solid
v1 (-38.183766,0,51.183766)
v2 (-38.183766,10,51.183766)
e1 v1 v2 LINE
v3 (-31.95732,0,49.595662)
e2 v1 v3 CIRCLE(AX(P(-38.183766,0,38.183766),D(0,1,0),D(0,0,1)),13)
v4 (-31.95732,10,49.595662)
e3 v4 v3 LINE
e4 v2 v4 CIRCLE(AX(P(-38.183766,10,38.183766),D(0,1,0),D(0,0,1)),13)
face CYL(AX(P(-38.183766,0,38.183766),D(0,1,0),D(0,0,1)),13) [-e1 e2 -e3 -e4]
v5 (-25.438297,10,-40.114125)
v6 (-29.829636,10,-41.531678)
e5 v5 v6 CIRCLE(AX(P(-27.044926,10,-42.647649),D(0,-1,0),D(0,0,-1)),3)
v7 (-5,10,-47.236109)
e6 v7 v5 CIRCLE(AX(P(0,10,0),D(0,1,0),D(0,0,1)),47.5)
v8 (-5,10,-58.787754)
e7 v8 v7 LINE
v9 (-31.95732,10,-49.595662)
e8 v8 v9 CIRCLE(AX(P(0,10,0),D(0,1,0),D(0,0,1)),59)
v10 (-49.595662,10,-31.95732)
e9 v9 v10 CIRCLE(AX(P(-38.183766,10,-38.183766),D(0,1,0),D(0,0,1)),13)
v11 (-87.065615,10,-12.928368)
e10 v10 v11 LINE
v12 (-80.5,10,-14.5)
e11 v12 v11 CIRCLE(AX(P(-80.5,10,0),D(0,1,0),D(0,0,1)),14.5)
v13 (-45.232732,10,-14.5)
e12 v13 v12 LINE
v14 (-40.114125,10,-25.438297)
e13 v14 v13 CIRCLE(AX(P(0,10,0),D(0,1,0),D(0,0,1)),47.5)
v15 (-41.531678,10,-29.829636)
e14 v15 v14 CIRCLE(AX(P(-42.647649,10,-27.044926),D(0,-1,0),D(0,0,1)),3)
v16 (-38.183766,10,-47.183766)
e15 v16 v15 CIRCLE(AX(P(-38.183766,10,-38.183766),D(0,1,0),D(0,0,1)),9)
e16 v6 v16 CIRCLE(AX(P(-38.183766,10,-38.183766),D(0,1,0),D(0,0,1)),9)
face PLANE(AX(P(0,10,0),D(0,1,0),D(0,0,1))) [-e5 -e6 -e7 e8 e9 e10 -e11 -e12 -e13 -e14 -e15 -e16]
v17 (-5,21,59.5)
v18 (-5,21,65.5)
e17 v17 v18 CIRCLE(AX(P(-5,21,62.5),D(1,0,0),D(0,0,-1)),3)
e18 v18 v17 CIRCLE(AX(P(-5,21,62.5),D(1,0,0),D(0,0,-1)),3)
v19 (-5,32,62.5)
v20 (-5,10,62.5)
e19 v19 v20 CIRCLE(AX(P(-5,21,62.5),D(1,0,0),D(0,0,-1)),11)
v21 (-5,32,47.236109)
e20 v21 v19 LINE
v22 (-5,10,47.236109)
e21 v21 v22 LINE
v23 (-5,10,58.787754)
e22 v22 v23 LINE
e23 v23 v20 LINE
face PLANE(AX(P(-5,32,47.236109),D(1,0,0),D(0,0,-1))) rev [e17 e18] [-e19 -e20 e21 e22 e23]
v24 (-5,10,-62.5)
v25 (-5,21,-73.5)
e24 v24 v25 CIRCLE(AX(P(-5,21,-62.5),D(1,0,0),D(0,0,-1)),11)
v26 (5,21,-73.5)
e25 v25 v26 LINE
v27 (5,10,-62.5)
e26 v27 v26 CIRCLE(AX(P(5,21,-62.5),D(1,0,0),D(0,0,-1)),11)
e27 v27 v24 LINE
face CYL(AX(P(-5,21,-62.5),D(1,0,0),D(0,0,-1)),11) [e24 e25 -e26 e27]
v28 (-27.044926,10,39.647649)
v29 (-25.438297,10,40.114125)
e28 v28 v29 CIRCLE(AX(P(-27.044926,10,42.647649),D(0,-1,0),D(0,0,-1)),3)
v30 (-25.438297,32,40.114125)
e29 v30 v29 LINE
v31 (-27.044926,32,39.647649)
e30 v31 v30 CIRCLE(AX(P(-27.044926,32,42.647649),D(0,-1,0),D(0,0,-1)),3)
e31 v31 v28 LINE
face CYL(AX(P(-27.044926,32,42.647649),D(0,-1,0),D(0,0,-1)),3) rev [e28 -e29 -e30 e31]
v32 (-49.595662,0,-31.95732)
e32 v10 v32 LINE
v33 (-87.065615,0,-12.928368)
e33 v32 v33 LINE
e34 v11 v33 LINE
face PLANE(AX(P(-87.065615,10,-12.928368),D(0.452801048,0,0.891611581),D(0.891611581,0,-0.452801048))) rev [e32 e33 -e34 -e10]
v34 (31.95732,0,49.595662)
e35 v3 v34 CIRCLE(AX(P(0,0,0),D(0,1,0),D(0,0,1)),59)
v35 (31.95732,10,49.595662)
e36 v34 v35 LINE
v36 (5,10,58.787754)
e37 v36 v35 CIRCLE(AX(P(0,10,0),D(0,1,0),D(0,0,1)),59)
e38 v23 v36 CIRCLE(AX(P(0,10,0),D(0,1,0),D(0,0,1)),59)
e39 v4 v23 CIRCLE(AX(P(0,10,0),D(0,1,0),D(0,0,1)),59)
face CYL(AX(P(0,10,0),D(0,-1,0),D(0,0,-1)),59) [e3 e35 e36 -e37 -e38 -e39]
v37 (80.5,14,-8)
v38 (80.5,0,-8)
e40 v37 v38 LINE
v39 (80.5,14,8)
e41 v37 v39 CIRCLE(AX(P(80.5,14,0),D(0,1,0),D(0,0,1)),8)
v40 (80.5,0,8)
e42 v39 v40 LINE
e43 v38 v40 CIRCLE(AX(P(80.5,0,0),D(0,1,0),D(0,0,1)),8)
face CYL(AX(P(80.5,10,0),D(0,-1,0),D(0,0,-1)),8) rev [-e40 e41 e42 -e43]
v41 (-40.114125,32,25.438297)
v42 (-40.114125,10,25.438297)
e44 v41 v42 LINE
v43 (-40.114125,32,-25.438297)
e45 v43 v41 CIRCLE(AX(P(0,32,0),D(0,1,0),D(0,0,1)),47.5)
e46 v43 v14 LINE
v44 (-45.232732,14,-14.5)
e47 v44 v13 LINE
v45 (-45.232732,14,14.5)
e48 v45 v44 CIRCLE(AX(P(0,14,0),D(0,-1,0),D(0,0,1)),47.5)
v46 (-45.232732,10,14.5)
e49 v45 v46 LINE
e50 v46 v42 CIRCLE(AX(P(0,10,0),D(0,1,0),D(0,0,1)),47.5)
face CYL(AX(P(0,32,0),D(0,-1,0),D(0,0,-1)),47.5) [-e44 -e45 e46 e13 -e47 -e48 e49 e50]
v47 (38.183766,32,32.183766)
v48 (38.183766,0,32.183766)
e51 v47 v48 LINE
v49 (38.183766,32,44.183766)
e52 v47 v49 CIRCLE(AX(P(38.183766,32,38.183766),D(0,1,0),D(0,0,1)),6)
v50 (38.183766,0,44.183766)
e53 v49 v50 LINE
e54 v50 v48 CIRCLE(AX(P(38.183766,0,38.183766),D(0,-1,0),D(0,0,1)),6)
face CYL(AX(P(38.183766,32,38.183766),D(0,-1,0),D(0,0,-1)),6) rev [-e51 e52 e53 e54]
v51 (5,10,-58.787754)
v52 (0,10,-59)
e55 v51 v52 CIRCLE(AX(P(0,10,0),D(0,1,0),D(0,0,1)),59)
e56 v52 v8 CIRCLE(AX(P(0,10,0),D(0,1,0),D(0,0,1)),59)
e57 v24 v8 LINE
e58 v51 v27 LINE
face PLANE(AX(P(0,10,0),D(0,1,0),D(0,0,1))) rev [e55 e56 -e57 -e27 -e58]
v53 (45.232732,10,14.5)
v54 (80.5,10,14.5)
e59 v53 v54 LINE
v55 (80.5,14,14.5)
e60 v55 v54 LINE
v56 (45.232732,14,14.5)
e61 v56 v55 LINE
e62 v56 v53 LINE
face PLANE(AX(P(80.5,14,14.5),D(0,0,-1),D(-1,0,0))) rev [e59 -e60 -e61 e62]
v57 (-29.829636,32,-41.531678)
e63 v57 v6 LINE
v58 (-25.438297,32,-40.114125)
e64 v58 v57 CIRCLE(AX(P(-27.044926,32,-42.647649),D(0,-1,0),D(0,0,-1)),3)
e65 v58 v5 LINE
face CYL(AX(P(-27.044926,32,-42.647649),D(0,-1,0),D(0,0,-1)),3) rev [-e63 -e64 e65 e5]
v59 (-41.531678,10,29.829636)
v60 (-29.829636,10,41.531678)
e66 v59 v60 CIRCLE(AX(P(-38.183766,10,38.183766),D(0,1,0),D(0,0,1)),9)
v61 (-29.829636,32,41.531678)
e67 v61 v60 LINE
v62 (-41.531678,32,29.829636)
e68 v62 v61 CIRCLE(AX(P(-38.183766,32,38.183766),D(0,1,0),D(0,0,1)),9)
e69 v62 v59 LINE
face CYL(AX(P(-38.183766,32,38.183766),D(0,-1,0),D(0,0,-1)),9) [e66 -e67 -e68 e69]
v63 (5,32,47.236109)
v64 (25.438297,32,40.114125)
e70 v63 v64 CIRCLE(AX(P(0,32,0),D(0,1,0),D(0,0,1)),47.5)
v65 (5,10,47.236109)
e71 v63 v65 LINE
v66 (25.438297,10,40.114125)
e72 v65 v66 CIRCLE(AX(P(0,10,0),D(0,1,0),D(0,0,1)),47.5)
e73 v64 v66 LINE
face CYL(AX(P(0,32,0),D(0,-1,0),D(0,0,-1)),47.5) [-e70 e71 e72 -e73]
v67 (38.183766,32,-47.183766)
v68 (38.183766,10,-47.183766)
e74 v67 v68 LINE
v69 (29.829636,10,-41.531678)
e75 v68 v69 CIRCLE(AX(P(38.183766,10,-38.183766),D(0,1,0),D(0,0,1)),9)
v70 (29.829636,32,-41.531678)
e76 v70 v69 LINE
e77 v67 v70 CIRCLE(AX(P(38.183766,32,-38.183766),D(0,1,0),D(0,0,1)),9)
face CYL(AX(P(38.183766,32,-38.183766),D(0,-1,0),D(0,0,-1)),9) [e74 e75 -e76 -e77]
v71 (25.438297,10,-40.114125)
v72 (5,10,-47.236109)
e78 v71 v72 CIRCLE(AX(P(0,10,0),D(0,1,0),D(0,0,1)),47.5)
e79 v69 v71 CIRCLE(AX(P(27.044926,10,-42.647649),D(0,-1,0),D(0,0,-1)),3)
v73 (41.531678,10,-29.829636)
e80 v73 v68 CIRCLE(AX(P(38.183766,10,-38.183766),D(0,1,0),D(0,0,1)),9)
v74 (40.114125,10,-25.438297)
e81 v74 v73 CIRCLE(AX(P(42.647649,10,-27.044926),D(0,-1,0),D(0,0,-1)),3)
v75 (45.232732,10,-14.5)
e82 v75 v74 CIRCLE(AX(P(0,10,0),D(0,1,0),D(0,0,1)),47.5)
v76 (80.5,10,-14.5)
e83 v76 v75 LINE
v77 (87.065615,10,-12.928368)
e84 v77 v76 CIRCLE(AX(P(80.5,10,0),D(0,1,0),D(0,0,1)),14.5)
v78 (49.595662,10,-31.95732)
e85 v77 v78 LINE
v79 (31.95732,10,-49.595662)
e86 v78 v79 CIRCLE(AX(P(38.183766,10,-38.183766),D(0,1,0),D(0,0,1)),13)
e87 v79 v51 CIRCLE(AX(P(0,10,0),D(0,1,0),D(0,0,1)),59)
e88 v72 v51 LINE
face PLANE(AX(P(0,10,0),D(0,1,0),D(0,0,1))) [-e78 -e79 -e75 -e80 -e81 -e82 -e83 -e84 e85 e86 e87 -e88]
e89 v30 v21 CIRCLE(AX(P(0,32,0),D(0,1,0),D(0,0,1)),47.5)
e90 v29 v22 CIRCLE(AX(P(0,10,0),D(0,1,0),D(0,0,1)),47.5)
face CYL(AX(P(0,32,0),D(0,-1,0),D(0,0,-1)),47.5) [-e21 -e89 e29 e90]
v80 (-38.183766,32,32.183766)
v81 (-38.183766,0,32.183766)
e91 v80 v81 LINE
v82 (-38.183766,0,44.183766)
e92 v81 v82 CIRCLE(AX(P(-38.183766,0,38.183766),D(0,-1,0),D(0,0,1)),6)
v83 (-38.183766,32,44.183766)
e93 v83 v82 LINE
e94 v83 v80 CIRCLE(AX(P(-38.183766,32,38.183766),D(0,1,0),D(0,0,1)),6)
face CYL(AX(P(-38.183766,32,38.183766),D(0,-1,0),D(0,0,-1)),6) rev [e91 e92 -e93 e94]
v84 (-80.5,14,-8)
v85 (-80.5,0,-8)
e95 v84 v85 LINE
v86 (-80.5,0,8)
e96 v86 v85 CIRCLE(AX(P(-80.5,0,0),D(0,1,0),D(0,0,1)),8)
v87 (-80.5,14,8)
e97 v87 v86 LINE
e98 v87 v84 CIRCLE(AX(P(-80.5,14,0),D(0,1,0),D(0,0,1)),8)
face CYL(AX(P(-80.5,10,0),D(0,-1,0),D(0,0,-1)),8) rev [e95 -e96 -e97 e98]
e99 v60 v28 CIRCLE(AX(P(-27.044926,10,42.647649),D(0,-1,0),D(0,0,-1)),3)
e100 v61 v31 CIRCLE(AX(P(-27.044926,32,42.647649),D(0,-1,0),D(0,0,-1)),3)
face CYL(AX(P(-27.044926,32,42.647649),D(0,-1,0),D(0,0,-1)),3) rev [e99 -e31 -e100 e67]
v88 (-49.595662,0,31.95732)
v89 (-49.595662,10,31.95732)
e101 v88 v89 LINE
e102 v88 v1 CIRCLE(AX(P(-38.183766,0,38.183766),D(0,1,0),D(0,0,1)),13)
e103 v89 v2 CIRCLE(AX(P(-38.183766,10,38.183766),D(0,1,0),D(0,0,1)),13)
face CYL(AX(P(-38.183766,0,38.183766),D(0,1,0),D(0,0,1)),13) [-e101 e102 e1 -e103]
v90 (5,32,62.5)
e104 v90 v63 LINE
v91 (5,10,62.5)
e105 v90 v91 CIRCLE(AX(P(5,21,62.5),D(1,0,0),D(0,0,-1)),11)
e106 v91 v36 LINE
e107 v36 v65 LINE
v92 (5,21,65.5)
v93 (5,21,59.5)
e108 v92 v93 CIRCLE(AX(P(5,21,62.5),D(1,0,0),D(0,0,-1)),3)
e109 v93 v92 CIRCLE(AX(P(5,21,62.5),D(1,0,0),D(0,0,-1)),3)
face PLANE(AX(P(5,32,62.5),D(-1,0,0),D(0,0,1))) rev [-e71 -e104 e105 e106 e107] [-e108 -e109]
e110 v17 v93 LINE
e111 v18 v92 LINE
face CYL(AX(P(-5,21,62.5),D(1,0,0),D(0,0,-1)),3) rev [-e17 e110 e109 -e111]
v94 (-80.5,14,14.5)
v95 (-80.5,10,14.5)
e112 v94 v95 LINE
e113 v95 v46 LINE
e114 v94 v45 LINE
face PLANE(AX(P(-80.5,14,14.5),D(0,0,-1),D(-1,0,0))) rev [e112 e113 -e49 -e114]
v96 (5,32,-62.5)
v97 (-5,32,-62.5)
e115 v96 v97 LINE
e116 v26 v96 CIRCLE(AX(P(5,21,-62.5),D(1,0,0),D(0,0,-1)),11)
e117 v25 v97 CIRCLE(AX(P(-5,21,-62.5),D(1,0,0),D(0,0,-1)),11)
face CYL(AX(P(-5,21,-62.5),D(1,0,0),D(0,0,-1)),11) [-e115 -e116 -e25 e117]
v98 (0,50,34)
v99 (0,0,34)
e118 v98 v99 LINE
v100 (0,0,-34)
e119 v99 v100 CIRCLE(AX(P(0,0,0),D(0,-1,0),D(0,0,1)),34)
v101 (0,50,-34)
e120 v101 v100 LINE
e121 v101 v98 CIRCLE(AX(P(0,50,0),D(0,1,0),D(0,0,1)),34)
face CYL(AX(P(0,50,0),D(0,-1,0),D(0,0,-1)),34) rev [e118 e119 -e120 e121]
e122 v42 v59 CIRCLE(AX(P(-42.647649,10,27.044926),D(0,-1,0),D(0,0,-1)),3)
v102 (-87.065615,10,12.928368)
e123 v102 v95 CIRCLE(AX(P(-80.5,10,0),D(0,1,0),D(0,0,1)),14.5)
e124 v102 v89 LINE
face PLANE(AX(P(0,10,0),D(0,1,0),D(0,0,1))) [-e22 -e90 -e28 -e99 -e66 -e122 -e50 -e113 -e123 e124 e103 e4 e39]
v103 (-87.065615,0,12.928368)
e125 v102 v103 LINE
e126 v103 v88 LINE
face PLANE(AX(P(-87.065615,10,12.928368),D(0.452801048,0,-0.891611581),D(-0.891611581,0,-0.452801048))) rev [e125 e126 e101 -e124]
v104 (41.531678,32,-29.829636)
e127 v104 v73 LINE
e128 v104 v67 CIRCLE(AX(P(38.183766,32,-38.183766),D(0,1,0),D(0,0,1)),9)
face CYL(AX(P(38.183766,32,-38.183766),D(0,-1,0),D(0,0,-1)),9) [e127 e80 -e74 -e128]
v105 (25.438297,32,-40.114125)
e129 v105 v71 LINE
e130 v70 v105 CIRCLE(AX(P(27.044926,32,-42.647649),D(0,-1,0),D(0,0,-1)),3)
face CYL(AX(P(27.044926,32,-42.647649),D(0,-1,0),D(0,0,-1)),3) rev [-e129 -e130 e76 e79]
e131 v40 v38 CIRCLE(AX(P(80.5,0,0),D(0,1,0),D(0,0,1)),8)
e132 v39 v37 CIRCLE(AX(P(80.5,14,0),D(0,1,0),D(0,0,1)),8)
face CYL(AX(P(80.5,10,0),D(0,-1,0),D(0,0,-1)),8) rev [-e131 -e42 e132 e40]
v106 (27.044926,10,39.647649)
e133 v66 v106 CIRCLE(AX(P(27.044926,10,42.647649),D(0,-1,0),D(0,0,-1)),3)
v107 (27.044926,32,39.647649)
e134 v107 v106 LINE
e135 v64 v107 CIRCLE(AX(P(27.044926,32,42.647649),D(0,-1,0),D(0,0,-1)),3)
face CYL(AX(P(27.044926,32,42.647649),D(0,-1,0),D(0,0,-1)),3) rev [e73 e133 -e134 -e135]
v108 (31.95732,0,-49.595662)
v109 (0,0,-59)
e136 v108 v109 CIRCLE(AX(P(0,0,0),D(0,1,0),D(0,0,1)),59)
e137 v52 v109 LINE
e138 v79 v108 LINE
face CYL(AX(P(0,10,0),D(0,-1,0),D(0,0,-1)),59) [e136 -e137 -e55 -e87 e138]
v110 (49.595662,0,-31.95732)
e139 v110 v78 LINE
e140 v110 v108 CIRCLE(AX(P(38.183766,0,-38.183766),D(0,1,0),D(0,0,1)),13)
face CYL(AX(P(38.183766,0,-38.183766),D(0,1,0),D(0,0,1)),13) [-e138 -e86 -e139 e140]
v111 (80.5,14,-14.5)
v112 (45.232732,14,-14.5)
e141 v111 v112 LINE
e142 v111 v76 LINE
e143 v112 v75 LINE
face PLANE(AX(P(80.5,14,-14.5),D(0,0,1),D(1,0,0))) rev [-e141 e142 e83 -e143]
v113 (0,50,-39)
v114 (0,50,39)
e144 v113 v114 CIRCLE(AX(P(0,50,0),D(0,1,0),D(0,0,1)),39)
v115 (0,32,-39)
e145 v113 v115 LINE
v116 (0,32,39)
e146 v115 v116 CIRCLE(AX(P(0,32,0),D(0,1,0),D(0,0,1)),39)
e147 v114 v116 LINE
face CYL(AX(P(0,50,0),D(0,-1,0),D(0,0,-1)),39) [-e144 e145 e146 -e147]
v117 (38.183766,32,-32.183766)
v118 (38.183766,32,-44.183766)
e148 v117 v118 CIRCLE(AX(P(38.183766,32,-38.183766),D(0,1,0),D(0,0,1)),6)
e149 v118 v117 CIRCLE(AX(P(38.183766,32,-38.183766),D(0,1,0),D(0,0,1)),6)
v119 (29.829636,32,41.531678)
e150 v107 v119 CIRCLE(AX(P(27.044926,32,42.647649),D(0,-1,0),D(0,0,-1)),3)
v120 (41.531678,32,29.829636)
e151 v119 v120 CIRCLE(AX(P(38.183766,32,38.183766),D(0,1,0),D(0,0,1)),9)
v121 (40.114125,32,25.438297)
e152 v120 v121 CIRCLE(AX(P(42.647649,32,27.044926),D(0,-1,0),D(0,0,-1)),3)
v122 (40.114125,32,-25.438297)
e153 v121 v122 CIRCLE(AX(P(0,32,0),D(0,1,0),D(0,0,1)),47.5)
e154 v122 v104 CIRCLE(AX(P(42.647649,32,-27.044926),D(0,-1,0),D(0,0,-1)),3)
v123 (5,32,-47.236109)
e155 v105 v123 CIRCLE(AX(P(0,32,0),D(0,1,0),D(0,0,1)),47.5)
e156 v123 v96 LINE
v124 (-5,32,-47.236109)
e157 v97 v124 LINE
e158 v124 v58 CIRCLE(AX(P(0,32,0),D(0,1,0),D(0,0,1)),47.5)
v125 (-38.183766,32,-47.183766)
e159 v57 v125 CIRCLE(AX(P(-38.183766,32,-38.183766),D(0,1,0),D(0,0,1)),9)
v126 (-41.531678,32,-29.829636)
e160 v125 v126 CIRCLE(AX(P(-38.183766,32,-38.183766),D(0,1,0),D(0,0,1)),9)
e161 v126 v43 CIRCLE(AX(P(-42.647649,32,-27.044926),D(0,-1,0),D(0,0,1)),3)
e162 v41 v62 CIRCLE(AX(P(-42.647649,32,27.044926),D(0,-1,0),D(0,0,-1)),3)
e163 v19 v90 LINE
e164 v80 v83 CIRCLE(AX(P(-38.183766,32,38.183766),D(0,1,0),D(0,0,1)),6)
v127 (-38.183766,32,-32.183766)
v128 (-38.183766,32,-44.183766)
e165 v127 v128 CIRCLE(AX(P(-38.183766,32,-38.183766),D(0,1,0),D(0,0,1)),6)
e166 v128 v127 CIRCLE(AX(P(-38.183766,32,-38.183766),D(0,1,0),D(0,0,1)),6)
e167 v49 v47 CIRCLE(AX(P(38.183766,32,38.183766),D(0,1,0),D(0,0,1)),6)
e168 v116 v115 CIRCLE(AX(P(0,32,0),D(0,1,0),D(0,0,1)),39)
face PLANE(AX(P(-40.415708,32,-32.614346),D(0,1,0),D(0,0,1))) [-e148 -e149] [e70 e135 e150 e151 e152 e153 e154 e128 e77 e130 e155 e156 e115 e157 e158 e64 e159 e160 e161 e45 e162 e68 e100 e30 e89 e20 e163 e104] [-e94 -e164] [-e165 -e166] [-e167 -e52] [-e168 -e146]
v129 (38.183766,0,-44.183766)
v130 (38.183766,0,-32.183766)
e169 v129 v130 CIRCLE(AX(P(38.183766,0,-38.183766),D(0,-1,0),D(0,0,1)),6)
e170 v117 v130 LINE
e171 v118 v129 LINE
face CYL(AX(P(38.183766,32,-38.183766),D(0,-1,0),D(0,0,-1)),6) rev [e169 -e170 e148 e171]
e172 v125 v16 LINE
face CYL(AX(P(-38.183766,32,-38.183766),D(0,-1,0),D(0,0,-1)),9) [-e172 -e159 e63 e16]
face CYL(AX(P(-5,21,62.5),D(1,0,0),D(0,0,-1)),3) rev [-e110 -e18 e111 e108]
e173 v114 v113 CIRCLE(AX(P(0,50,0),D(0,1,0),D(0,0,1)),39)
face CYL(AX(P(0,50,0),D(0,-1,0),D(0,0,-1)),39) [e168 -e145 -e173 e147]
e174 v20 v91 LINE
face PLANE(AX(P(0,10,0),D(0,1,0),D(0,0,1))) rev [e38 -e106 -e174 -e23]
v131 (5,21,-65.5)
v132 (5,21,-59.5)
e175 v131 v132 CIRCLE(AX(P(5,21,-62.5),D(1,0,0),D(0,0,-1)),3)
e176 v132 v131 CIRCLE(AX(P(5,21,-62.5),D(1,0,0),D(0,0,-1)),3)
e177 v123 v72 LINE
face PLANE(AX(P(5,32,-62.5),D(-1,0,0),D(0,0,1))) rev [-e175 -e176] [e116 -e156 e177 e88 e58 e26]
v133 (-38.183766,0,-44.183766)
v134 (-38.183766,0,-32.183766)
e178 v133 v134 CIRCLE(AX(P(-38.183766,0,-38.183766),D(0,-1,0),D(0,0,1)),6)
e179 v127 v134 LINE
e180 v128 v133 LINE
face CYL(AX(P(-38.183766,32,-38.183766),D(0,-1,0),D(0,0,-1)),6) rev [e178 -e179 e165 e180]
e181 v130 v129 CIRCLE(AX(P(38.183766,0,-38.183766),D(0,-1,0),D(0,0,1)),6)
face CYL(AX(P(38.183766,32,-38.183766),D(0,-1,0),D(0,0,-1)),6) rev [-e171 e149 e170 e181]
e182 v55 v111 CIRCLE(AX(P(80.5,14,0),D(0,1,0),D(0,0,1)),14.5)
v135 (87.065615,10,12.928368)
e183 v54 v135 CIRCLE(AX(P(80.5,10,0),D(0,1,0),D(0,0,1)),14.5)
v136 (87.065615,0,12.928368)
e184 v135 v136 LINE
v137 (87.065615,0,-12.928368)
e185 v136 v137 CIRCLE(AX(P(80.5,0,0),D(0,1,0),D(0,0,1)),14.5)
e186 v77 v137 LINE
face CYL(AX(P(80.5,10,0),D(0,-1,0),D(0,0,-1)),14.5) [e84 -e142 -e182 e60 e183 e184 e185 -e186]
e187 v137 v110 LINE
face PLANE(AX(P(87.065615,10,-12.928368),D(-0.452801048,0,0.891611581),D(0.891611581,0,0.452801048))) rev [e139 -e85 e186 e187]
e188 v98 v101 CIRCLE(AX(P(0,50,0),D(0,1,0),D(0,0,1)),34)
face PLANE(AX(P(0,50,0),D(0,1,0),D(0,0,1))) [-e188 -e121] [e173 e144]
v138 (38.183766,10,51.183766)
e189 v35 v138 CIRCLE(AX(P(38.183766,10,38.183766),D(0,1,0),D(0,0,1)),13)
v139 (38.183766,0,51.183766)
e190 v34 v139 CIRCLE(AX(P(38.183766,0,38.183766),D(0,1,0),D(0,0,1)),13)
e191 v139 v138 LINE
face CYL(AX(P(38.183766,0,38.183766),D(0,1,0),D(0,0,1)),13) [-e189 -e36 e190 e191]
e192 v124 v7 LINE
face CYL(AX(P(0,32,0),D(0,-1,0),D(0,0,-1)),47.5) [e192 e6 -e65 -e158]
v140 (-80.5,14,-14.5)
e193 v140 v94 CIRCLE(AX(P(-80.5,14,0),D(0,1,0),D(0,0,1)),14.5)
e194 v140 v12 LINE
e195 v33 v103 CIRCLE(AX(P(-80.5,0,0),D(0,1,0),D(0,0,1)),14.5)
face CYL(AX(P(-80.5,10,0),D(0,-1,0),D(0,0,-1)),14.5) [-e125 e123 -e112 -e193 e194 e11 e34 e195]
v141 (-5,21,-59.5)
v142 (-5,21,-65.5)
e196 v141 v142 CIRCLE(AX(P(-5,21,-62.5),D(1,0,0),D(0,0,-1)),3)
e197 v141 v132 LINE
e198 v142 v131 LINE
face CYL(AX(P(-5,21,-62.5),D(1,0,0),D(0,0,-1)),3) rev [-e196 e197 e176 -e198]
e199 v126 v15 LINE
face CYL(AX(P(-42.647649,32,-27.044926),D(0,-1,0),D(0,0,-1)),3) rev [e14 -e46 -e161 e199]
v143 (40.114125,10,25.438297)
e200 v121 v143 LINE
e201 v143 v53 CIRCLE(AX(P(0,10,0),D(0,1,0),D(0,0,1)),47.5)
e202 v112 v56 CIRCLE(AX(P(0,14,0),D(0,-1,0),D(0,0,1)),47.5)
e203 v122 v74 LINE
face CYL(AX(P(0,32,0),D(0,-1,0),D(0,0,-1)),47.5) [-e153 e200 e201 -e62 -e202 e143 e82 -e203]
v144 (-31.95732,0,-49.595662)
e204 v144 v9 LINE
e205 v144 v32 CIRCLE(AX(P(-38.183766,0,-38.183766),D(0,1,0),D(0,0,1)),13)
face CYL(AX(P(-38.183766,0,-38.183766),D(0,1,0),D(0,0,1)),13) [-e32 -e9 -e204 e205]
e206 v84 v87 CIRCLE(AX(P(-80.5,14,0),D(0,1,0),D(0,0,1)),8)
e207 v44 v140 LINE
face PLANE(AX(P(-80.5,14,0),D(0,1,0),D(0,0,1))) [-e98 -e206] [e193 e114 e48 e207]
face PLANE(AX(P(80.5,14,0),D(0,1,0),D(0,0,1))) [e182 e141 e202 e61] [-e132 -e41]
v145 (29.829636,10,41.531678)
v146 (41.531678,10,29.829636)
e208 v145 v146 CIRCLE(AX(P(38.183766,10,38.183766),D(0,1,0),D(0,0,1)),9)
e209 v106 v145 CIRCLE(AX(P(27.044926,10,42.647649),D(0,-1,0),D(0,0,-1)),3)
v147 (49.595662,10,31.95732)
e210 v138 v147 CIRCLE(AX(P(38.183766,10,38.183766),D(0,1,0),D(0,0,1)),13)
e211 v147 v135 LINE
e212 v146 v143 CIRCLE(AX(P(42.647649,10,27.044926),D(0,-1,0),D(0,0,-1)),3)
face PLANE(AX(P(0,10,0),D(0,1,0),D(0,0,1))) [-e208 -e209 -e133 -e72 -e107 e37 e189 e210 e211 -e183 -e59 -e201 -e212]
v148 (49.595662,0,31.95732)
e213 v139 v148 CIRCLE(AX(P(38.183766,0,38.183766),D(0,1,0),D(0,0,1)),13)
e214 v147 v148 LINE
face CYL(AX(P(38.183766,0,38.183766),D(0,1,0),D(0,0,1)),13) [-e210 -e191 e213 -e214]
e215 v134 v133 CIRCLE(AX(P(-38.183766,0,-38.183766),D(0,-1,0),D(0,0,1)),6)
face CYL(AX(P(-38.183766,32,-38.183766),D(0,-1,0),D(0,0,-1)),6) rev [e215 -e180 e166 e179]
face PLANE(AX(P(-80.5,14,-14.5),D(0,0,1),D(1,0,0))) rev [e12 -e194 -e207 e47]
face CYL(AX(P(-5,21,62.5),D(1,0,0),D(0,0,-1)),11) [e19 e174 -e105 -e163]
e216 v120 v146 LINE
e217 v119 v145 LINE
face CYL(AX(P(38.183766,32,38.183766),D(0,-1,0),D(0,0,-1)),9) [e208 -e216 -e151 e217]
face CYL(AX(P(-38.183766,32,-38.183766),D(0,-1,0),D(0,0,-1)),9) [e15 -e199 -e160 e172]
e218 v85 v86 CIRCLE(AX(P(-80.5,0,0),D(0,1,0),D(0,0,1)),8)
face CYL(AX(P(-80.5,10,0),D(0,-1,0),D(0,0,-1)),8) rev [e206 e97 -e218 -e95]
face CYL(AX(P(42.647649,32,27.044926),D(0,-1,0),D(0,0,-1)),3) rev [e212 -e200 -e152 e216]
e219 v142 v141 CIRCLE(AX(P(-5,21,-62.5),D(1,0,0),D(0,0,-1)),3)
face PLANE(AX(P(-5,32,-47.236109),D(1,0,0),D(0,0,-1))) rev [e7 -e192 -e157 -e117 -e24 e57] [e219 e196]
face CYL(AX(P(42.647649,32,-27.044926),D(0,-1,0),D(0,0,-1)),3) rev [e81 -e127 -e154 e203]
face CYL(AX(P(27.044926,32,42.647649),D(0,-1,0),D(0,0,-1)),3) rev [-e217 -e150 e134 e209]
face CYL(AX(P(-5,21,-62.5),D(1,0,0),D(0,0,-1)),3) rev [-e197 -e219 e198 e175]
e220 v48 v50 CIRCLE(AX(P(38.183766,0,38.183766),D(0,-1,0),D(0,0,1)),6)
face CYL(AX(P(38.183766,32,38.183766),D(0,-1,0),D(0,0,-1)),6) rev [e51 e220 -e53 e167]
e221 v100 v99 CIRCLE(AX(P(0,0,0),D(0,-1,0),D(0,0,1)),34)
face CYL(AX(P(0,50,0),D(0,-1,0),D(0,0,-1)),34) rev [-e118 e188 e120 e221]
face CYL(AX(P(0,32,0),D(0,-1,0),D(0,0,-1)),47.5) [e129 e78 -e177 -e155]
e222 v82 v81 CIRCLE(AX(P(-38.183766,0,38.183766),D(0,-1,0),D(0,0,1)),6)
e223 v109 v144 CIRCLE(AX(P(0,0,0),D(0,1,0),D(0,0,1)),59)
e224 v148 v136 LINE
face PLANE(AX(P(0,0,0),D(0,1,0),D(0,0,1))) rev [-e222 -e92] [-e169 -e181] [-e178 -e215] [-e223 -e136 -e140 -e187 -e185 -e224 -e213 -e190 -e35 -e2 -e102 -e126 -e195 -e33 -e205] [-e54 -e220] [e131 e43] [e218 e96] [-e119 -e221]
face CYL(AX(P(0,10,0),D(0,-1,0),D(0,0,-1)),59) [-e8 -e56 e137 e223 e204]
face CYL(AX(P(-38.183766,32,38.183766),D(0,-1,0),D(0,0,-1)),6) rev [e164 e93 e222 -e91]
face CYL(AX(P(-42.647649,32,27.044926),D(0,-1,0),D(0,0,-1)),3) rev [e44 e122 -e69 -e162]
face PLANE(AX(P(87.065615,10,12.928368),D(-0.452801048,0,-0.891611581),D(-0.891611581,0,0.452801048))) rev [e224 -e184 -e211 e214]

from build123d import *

# Parameters (mm, degrees)
BASE_FLANGE_SKETCH_R       = 59
BASE_FLANGE_118_DEPTH      = 10
FLANGE_LOBES_SKETCH_R      = 13
FLANGE_LOBES_DEPTH         = 10
HUB_AND_BOSSES_SKETCH_R    = 6
HUB_WITH_BOLT_BOSSES_DEPTH = 22
PIPE_COLLAR_SKETCH_R       = 39
PIPE_COLLAR_SKETCH_R_2     = 34
PIPE_COLLAR_78_DEPTH       = 18
SIDE_LUGS_DEPTH            = 22
LUG_GUSSET_A_SKETCH_R      = 3
LUG_GUSSET_A_DEPTH         = 10
LUG_HOLE_A_SKETCH_R        = 3
LUG_HOLE_A_DEPTH           = 10
LUG_GUSSET_B_SKETCH_R      = 3
LUG_GUSSET_B_DEPTH         = 10
LUG_HOLE_B_SKETCH_R        = 3
LUG_HOLE_B_DEPTH           = 10
MOUNTING_EARS_SKETCH_R     = 8
MOUNTING_EARS_DEPTH        = 10
EAR_RIB_A_SKETCH_R         = 8
EAR_RIB_A_DEPTH            = 4
EAR_RIB_B_SKETCH_R         = 8
EAR_RIB_B_DEPTH            = 4
SIDE_RELIEF_CUT_REACH      = 126.303
SIDE_RELIEF_CUT_SKETCH_R   = 6
PIPE_BORE_REACH            = 126.303
PIPE_BORE_SKETCH_R         = 34


with BuildPart() as part:
    # Base Flange Sketch → Base Flange Ø118 (new body)
    with BuildSketch(Plane(origin=(0, 0, 0), x_dir=(1, 0, 0), z_dir=(0, 1, 0))):
        with Locations(Location((0, 0, 0), (0, 0, 270))):
            Circle(BASE_FLANGE_SKETCH_R)
    extrude(amount=BASE_FLANGE_118_DEPTH)

    # Flange Lobes Sketch → Flange Lobes (add)
    with BuildSketch(Plane(origin=(0, 10, 0), x_dir=(1, 0, 0), z_dir=(0, 1, 0))):
        with Locations((-38.183766184, 38.183766184)):
            Circle(FLANGE_LOBES_SKETCH_R)
        with Locations((38.183766184, 38.183766184)):
            Circle(FLANGE_LOBES_SKETCH_R)
        with Locations((38.183766184, -38.183766184)):
            Circle(FLANGE_LOBES_SKETCH_R)
        with Locations((-38.183766184, -38.183766184)):
            Circle(FLANGE_LOBES_SKETCH_R)
    extrude(amount=-FLANGE_LOBES_DEPTH)

    # Hub and Bosses Sketch → Hub with Bolt Bosses (add)
    with BuildSketch(Plane(origin=(0, 10, 0), x_dir=(1, 0, 0), z_dir=(0, 1, 0))):
        with BuildLine():
            ThreePointArc((-40.114125183, 25.438297128), (-47.5, 0), (-40.114125183, -25.438297128))
            ThreePointArc((-40.114125183, -25.438297128), (-39.792711515, -27.966518872), (-41.531678205, -29.829636361))
            ThreePointArc((-41.531678205, -29.829636361), (-44.547727215, -44.547727215), (-29.829636361, -41.531678205))
            ThreePointArc((-29.829636361, -41.531678205), (-27.966518872, -39.792711515), (-25.438297128, -40.114125183))
            ThreePointArc((-25.438297128, -40.114125183), (0, -47.5), (25.438297128, -40.114125183))
            ThreePointArc((25.438297128, -40.114125183), (27.966518872, -39.792711515), (29.829636361, -41.531678205))
            ThreePointArc((29.829636361, -41.531678205), (44.547727215, -44.547727215), (41.531678205, -29.829636361))
            ThreePointArc((41.531678205, -29.829636361), (39.792711515, -27.966518872), (40.114125183, -25.438297128))
            ThreePointArc((40.114125183, -25.438297128), (47.5, 0), (40.114125183, 25.438297128))
            ThreePointArc((40.114125183, 25.438297128), (39.792711515, 27.966518872), (41.531678205, 29.829636361))
            ThreePointArc((41.531678205, 29.829636361), (44.547727215, 44.547727215), (29.829636361, 41.531678205))
            ThreePointArc((29.829636361, 41.531678205), (27.966518872, 39.792711515), (25.438297128, 40.114125183))
            ThreePointArc((25.438297128, 40.114125183), (0, 47.5), (-25.438297128, 40.114125183))
            ThreePointArc((-25.438297128, 40.114125183), (-27.966518872, 39.792711515), (-29.829636361, 41.531678205))
            ThreePointArc((-29.829636361, 41.531678205), (-44.547727215, 44.547727215), (-41.531678205, 29.829636361))
            ThreePointArc((-41.531678205, 29.829636361), (-39.792711515, 27.966518872), (-40.114125183, 25.438297128))
        make_face()
        with Locations(Location((-38.183766184, 38.183766184, 0), (0, 0, 270))):
            Circle(HUB_AND_BOSSES_SKETCH_R, mode=Mode.SUBTRACT)
        with Locations(Location((38.183766184, 38.183766184, 0), (0, 0, 270))):
            Circle(HUB_AND_BOSSES_SKETCH_R, mode=Mode.SUBTRACT)
        with Locations(Location((38.183766184, -38.183766184, 0), (0, 0, 270))):
            Circle(HUB_AND_BOSSES_SKETCH_R, mode=Mode.SUBTRACT)
        with Locations(Location((-38.183766184, -38.183766184, 0), (0, 0, 270))):
            Circle(HUB_AND_BOSSES_SKETCH_R, mode=Mode.SUBTRACT)
    extrude(amount=HUB_WITH_BOLT_BOSSES_DEPTH)

    # Pipe Collar Sketch → Pipe Collar Ø78 (add)
    with BuildSketch(Plane(origin=(0, 32, 0), x_dir=(1, 0, 0), z_dir=(0, 1, 0))):
        with Locations(Location((0, 0, 0), (0, 0, 270))):
            Circle(PIPE_COLLAR_SKETCH_R)
        with Locations(Location((0, 0, 0), (0, 0, 270))):
            Circle(PIPE_COLLAR_SKETCH_R_2, mode=Mode.SUBTRACT)
    extrude(amount=PIPE_COLLAR_78_DEPTH)

    # Side Lugs Sketch → Side Lugs (add)
    with BuildSketch(Plane(origin=(0, 10, 0), x_dir=(1, 0, 0), z_dir=(0, 1, 0))):
        with BuildLine():
            Line((-5, -47.236109069), (-5, -62.5))
            Line((-5, -62.5), (5, -62.5))
            Line((5, -62.5), (5, -47.236109069))
            ThreePointArc((5, -47.236109069), (0, -47.5), (-5, -47.236109069))
        make_face()
        with BuildLine():
            Line((-5, 47.236109069), (-5, 62.5))
            Line((-5, 62.5), (5, 62.5))
            Line((5, 62.5), (5, 47.236109069))
            ThreePointArc((5, 47.236109069), (0, 47.5), (-5, 47.236109069))
        make_face()
    extrude(amount=SIDE_LUGS_DEPTH)

    # Lug Gusset A Sketch → Lug Gusset A (add)
    with BuildSketch(Plane(origin=(5, 0, 0), x_dir=(0, 0, -1), z_dir=(1, 0, 0))):
        with BuildLine():
            Line((-62.5, 32), (-47.236109069, 32))
            Line((-47.236109069, 32), (-47.183766184, 10))
            Line((-47.183766184, 10), (-62.5, 10))
            ThreePointArc((-62.5, 10), (-73.5, 21), (-62.5, 32))
        make_face()
        with Locations((-62.5, 21)):
            Circle(LUG_GUSSET_A_SKETCH_R, mode=Mode.SUBTRACT)
    extrude(amount=-LUG_GUSSET_A_DEPTH)

    # Lug Hole A Sketch → Lug Hole A (cut)
    with BuildSketch(Plane(origin=(5, 0, 0), x_dir=(0, 0, -1), z_dir=(1, 0, 0))):
        with Locations((-62.5, 21)):
            Circle(LUG_HOLE_A_SKETCH_R)
    extrude(amount=-LUG_HOLE_A_DEPTH, mode=Mode.SUBTRACT)

    # Lug Gusset B Sketch → Lug Gusset B (add)
    with BuildSketch(Plane(origin=(5, 0, 0), x_dir=(0, 0, -1), z_dir=(1, 0, 0))):
        with BuildLine():
            Line((62.5, 32), (47.183766184, 32))
            Line((47.183766184, 32), (47.236109069, 10))
            Line((47.236109069, 10), (62.5, 10))
            ThreePointArc((62.5, 10), (73.5, 21), (62.5, 32))
        make_face()
        with Locations((62.5, 21)):
            Circle(LUG_GUSSET_B_SKETCH_R, mode=Mode.SUBTRACT)
    extrude(amount=-LUG_GUSSET_B_DEPTH)

    # Lug Hole B Sketch → Lug Hole B (cut)
    with BuildSketch(Plane(origin=(5, 0, 0), x_dir=(0, 0, -1), z_dir=(1, 0, 0))):
        with Locations((62.5, 21)):
            Circle(LUG_HOLE_B_SKETCH_R)
    extrude(amount=-LUG_HOLE_B_DEPTH, mode=Mode.SUBTRACT)

    # Mounting Ears Sketch → Mounting Ears (add)
    # profile 1 of 2: a face of its own
    with BuildSketch(Plane(origin=(0, 0, 0), x_dir=(1, 0, 0), z_dir=(0, 1, 0))):
        with BuildLine():
            Line((-87.065615201, 12.928367918), (-49.595662085, 31.957320012))
            ThreePointArc((-49.595662085, 31.957320012), (-59, 0), (-49.595662085, -31.957320012))
            Line((-49.595662085, -31.957320012), (-87.065615201, -12.928367918))
            ThreePointArc((-87.065615201, -12.928367918), (-95, 0), (-87.065615201, 12.928367918))
        make_face()
        with Locations(Location((-80.5, 0, 0), (0, 0, 270))):
            Circle(MOUNTING_EARS_SKETCH_R, mode=Mode.SUBTRACT)
    # profile 2 of 2: a face of its own
    with BuildSketch(Plane(origin=(0, 0, 0), x_dir=(1, 0, 0), z_dir=(0, 1, 0))):
        with BuildLine():
            Line((87.065615201, 12.928367918), (49.595662085, 31.957320012))
            ThreePointArc((49.595662085, 31.957320012), (59, 0), (49.595662085, -31.957320012))
            Line((49.595662085, -31.957320012), (87.065615201, -12.928367918))
            ThreePointArc((87.065615201, -12.928367918), (95, 0), (87.065615201, 12.928367918))
        make_face()
        with Locations(Location((80.5, 0, 0), (0, 0, 270))):
            Circle(MOUNTING_EARS_SKETCH_R, mode=Mode.SUBTRACT)
    extrude(amount=MOUNTING_EARS_DEPTH)

    # Ear Rib A Sketch → Ear Rib A (add)
    with BuildSketch(Plane(origin=(0, 10, 0), x_dir=(1, 0, 0), z_dir=(0, 1, 0))):
        with BuildLine():
            Line((-80.5, 14.5), (-45.232731512, 14.5))
            ThreePointArc((-45.232731512, 14.5), (-47.5, 0), (-45.232731512, -14.5))
            Line((-45.232731512, -14.5), (-80.5, -14.5))
            ThreePointArc((-80.5, -14.5), (-95, 0), (-80.5, 14.5))
        make_face()
        with Locations(Location((-80.5, 0, 0), (0, 0, 270))):
            Circle(EAR_RIB_A_SKETCH_R, mode=Mode.SUBTRACT)
    extrude(amount=EAR_RIB_A_DEPTH)

    # Ear Rib B Sketch → Ear Rib B (add)
    with BuildSketch(Plane(origin=(0, 10, 0), x_dir=(1, 0, 0), z_dir=(0, 1, 0))):
        with BuildLine():
            Line((80.5, 14.5), (45.232731512, 14.5))
            ThreePointArc((45.232731512, 14.5), (47.5, 0), (45.232731512, -14.5))
            Line((45.232731512, -14.5), (80.5, -14.5))
            ThreePointArc((80.5, -14.5), (95, 0), (80.5, 14.5))
        make_face()
        with Locations(Location((80.5, 0, 0), (0, 0, 270))):
            Circle(EAR_RIB_B_SKETCH_R, mode=Mode.SUBTRACT)
    extrude(amount=EAR_RIB_B_DEPTH)

    # Side Relief Cut Sketch → Side Relief Cut (cut, up to next)
    with BuildSketch(Plane(origin=(0, 32, 0), x_dir=(1, 0, 0), z_dir=(0, 1, 0)), mode=Mode.PRIVATE) as side_relief_cut_sk1:
        with Locations(Location((-38.183766184, 38.183766184, 0), (0, 0, 270))):
            Circle(SIDE_RELIEF_CUT_SKETCH_R)
    side_relief_cut_tool1 = extrude(side_relief_cut_sk1.sketch, amount=-SIDE_RELIEF_CUT_REACH, mode=Mode.PRIVATE) & part.part
    # Side Relief Cut Sketch → Side Relief Cut (cut, up to next)
    with BuildSketch(Plane(origin=(0, 32, 0), x_dir=(1, 0, 0), z_dir=(0, 1, 0)), mode=Mode.PRIVATE) as side_relief_cut_sk2:
        with Locations(Location((38.183766184, 38.183766184, 0), (0, 0, 270))):
            Circle(SIDE_RELIEF_CUT_SKETCH_R)
    side_relief_cut_tool2 = extrude(side_relief_cut_sk2.sketch, amount=-SIDE_RELIEF_CUT_REACH, mode=Mode.PRIVATE) & part.part
    # Side Relief Cut Sketch → Side Relief Cut (cut, up to next)
    with BuildSketch(Plane(origin=(0, 32, 0), x_dir=(1, 0, 0), z_dir=(0, 1, 0)), mode=Mode.PRIVATE) as side_relief_cut_sk3:
        with Locations(Location((38.183766184, -38.183766184, 0), (0, 0, 270))):
            Circle(SIDE_RELIEF_CUT_SKETCH_R)
    side_relief_cut_tool3 = extrude(side_relief_cut_sk3.sketch, amount=-SIDE_RELIEF_CUT_REACH, mode=Mode.PRIVATE) & part.part
    # Side Relief Cut Sketch → Side Relief Cut (cut, up to next)
    with BuildSketch(Plane(origin=(0, 32, 0), x_dir=(1, 0, 0), z_dir=(0, 1, 0)), mode=Mode.PRIVATE) as side_relief_cut_sk4:
        with Locations(Location((-38.183766184, -38.183766184, 0), (0, 0, 270))):
            Circle(SIDE_RELIEF_CUT_SKETCH_R)
    side_relief_cut_tool4 = extrude(side_relief_cut_sk4.sketch, amount=-SIDE_RELIEF_CUT_REACH, mode=Mode.PRIVATE) & part.part
    add(side_relief_cut_tool1.solids().sort_by_distance((-38.183766, 32, -38.183766))[0], mode=Mode.SUBTRACT)
    add(side_relief_cut_tool2.solids().sort_by_distance((38.183766, 32, -38.183766))[0], mode=Mode.SUBTRACT)
    add(side_relief_cut_tool3.solids().sort_by_distance((38.183766, 32, 38.183766))[0], mode=Mode.SUBTRACT)
    add(side_relief_cut_tool4.solids().sort_by_distance((-38.183766, 32, 38.183766))[0], mode=Mode.SUBTRACT)

    # Pipe Bore Sketch → Pipe Bore (cut, up to next)
    with BuildSketch(Plane(origin=(0, 32, 0), x_dir=(1, 0, 0), z_dir=(0, 1, 0)), mode=Mode.PRIVATE) as pipe_bore_sk1:
        with Locations(Location((0, 0, 0), (0, 0, 270))):
            Circle(PIPE_BORE_SKETCH_R)
    pipe_bore_tool1 = extrude(pipe_bore_sk1.sketch, amount=-PIPE_BORE_REACH, mode=Mode.PRIVATE) & part.part
    add(pipe_bore_tool1.solids().sort_by_distance((0, 32, 0))[0], mode=Mode.SUBTRACT)


solid = part.part
